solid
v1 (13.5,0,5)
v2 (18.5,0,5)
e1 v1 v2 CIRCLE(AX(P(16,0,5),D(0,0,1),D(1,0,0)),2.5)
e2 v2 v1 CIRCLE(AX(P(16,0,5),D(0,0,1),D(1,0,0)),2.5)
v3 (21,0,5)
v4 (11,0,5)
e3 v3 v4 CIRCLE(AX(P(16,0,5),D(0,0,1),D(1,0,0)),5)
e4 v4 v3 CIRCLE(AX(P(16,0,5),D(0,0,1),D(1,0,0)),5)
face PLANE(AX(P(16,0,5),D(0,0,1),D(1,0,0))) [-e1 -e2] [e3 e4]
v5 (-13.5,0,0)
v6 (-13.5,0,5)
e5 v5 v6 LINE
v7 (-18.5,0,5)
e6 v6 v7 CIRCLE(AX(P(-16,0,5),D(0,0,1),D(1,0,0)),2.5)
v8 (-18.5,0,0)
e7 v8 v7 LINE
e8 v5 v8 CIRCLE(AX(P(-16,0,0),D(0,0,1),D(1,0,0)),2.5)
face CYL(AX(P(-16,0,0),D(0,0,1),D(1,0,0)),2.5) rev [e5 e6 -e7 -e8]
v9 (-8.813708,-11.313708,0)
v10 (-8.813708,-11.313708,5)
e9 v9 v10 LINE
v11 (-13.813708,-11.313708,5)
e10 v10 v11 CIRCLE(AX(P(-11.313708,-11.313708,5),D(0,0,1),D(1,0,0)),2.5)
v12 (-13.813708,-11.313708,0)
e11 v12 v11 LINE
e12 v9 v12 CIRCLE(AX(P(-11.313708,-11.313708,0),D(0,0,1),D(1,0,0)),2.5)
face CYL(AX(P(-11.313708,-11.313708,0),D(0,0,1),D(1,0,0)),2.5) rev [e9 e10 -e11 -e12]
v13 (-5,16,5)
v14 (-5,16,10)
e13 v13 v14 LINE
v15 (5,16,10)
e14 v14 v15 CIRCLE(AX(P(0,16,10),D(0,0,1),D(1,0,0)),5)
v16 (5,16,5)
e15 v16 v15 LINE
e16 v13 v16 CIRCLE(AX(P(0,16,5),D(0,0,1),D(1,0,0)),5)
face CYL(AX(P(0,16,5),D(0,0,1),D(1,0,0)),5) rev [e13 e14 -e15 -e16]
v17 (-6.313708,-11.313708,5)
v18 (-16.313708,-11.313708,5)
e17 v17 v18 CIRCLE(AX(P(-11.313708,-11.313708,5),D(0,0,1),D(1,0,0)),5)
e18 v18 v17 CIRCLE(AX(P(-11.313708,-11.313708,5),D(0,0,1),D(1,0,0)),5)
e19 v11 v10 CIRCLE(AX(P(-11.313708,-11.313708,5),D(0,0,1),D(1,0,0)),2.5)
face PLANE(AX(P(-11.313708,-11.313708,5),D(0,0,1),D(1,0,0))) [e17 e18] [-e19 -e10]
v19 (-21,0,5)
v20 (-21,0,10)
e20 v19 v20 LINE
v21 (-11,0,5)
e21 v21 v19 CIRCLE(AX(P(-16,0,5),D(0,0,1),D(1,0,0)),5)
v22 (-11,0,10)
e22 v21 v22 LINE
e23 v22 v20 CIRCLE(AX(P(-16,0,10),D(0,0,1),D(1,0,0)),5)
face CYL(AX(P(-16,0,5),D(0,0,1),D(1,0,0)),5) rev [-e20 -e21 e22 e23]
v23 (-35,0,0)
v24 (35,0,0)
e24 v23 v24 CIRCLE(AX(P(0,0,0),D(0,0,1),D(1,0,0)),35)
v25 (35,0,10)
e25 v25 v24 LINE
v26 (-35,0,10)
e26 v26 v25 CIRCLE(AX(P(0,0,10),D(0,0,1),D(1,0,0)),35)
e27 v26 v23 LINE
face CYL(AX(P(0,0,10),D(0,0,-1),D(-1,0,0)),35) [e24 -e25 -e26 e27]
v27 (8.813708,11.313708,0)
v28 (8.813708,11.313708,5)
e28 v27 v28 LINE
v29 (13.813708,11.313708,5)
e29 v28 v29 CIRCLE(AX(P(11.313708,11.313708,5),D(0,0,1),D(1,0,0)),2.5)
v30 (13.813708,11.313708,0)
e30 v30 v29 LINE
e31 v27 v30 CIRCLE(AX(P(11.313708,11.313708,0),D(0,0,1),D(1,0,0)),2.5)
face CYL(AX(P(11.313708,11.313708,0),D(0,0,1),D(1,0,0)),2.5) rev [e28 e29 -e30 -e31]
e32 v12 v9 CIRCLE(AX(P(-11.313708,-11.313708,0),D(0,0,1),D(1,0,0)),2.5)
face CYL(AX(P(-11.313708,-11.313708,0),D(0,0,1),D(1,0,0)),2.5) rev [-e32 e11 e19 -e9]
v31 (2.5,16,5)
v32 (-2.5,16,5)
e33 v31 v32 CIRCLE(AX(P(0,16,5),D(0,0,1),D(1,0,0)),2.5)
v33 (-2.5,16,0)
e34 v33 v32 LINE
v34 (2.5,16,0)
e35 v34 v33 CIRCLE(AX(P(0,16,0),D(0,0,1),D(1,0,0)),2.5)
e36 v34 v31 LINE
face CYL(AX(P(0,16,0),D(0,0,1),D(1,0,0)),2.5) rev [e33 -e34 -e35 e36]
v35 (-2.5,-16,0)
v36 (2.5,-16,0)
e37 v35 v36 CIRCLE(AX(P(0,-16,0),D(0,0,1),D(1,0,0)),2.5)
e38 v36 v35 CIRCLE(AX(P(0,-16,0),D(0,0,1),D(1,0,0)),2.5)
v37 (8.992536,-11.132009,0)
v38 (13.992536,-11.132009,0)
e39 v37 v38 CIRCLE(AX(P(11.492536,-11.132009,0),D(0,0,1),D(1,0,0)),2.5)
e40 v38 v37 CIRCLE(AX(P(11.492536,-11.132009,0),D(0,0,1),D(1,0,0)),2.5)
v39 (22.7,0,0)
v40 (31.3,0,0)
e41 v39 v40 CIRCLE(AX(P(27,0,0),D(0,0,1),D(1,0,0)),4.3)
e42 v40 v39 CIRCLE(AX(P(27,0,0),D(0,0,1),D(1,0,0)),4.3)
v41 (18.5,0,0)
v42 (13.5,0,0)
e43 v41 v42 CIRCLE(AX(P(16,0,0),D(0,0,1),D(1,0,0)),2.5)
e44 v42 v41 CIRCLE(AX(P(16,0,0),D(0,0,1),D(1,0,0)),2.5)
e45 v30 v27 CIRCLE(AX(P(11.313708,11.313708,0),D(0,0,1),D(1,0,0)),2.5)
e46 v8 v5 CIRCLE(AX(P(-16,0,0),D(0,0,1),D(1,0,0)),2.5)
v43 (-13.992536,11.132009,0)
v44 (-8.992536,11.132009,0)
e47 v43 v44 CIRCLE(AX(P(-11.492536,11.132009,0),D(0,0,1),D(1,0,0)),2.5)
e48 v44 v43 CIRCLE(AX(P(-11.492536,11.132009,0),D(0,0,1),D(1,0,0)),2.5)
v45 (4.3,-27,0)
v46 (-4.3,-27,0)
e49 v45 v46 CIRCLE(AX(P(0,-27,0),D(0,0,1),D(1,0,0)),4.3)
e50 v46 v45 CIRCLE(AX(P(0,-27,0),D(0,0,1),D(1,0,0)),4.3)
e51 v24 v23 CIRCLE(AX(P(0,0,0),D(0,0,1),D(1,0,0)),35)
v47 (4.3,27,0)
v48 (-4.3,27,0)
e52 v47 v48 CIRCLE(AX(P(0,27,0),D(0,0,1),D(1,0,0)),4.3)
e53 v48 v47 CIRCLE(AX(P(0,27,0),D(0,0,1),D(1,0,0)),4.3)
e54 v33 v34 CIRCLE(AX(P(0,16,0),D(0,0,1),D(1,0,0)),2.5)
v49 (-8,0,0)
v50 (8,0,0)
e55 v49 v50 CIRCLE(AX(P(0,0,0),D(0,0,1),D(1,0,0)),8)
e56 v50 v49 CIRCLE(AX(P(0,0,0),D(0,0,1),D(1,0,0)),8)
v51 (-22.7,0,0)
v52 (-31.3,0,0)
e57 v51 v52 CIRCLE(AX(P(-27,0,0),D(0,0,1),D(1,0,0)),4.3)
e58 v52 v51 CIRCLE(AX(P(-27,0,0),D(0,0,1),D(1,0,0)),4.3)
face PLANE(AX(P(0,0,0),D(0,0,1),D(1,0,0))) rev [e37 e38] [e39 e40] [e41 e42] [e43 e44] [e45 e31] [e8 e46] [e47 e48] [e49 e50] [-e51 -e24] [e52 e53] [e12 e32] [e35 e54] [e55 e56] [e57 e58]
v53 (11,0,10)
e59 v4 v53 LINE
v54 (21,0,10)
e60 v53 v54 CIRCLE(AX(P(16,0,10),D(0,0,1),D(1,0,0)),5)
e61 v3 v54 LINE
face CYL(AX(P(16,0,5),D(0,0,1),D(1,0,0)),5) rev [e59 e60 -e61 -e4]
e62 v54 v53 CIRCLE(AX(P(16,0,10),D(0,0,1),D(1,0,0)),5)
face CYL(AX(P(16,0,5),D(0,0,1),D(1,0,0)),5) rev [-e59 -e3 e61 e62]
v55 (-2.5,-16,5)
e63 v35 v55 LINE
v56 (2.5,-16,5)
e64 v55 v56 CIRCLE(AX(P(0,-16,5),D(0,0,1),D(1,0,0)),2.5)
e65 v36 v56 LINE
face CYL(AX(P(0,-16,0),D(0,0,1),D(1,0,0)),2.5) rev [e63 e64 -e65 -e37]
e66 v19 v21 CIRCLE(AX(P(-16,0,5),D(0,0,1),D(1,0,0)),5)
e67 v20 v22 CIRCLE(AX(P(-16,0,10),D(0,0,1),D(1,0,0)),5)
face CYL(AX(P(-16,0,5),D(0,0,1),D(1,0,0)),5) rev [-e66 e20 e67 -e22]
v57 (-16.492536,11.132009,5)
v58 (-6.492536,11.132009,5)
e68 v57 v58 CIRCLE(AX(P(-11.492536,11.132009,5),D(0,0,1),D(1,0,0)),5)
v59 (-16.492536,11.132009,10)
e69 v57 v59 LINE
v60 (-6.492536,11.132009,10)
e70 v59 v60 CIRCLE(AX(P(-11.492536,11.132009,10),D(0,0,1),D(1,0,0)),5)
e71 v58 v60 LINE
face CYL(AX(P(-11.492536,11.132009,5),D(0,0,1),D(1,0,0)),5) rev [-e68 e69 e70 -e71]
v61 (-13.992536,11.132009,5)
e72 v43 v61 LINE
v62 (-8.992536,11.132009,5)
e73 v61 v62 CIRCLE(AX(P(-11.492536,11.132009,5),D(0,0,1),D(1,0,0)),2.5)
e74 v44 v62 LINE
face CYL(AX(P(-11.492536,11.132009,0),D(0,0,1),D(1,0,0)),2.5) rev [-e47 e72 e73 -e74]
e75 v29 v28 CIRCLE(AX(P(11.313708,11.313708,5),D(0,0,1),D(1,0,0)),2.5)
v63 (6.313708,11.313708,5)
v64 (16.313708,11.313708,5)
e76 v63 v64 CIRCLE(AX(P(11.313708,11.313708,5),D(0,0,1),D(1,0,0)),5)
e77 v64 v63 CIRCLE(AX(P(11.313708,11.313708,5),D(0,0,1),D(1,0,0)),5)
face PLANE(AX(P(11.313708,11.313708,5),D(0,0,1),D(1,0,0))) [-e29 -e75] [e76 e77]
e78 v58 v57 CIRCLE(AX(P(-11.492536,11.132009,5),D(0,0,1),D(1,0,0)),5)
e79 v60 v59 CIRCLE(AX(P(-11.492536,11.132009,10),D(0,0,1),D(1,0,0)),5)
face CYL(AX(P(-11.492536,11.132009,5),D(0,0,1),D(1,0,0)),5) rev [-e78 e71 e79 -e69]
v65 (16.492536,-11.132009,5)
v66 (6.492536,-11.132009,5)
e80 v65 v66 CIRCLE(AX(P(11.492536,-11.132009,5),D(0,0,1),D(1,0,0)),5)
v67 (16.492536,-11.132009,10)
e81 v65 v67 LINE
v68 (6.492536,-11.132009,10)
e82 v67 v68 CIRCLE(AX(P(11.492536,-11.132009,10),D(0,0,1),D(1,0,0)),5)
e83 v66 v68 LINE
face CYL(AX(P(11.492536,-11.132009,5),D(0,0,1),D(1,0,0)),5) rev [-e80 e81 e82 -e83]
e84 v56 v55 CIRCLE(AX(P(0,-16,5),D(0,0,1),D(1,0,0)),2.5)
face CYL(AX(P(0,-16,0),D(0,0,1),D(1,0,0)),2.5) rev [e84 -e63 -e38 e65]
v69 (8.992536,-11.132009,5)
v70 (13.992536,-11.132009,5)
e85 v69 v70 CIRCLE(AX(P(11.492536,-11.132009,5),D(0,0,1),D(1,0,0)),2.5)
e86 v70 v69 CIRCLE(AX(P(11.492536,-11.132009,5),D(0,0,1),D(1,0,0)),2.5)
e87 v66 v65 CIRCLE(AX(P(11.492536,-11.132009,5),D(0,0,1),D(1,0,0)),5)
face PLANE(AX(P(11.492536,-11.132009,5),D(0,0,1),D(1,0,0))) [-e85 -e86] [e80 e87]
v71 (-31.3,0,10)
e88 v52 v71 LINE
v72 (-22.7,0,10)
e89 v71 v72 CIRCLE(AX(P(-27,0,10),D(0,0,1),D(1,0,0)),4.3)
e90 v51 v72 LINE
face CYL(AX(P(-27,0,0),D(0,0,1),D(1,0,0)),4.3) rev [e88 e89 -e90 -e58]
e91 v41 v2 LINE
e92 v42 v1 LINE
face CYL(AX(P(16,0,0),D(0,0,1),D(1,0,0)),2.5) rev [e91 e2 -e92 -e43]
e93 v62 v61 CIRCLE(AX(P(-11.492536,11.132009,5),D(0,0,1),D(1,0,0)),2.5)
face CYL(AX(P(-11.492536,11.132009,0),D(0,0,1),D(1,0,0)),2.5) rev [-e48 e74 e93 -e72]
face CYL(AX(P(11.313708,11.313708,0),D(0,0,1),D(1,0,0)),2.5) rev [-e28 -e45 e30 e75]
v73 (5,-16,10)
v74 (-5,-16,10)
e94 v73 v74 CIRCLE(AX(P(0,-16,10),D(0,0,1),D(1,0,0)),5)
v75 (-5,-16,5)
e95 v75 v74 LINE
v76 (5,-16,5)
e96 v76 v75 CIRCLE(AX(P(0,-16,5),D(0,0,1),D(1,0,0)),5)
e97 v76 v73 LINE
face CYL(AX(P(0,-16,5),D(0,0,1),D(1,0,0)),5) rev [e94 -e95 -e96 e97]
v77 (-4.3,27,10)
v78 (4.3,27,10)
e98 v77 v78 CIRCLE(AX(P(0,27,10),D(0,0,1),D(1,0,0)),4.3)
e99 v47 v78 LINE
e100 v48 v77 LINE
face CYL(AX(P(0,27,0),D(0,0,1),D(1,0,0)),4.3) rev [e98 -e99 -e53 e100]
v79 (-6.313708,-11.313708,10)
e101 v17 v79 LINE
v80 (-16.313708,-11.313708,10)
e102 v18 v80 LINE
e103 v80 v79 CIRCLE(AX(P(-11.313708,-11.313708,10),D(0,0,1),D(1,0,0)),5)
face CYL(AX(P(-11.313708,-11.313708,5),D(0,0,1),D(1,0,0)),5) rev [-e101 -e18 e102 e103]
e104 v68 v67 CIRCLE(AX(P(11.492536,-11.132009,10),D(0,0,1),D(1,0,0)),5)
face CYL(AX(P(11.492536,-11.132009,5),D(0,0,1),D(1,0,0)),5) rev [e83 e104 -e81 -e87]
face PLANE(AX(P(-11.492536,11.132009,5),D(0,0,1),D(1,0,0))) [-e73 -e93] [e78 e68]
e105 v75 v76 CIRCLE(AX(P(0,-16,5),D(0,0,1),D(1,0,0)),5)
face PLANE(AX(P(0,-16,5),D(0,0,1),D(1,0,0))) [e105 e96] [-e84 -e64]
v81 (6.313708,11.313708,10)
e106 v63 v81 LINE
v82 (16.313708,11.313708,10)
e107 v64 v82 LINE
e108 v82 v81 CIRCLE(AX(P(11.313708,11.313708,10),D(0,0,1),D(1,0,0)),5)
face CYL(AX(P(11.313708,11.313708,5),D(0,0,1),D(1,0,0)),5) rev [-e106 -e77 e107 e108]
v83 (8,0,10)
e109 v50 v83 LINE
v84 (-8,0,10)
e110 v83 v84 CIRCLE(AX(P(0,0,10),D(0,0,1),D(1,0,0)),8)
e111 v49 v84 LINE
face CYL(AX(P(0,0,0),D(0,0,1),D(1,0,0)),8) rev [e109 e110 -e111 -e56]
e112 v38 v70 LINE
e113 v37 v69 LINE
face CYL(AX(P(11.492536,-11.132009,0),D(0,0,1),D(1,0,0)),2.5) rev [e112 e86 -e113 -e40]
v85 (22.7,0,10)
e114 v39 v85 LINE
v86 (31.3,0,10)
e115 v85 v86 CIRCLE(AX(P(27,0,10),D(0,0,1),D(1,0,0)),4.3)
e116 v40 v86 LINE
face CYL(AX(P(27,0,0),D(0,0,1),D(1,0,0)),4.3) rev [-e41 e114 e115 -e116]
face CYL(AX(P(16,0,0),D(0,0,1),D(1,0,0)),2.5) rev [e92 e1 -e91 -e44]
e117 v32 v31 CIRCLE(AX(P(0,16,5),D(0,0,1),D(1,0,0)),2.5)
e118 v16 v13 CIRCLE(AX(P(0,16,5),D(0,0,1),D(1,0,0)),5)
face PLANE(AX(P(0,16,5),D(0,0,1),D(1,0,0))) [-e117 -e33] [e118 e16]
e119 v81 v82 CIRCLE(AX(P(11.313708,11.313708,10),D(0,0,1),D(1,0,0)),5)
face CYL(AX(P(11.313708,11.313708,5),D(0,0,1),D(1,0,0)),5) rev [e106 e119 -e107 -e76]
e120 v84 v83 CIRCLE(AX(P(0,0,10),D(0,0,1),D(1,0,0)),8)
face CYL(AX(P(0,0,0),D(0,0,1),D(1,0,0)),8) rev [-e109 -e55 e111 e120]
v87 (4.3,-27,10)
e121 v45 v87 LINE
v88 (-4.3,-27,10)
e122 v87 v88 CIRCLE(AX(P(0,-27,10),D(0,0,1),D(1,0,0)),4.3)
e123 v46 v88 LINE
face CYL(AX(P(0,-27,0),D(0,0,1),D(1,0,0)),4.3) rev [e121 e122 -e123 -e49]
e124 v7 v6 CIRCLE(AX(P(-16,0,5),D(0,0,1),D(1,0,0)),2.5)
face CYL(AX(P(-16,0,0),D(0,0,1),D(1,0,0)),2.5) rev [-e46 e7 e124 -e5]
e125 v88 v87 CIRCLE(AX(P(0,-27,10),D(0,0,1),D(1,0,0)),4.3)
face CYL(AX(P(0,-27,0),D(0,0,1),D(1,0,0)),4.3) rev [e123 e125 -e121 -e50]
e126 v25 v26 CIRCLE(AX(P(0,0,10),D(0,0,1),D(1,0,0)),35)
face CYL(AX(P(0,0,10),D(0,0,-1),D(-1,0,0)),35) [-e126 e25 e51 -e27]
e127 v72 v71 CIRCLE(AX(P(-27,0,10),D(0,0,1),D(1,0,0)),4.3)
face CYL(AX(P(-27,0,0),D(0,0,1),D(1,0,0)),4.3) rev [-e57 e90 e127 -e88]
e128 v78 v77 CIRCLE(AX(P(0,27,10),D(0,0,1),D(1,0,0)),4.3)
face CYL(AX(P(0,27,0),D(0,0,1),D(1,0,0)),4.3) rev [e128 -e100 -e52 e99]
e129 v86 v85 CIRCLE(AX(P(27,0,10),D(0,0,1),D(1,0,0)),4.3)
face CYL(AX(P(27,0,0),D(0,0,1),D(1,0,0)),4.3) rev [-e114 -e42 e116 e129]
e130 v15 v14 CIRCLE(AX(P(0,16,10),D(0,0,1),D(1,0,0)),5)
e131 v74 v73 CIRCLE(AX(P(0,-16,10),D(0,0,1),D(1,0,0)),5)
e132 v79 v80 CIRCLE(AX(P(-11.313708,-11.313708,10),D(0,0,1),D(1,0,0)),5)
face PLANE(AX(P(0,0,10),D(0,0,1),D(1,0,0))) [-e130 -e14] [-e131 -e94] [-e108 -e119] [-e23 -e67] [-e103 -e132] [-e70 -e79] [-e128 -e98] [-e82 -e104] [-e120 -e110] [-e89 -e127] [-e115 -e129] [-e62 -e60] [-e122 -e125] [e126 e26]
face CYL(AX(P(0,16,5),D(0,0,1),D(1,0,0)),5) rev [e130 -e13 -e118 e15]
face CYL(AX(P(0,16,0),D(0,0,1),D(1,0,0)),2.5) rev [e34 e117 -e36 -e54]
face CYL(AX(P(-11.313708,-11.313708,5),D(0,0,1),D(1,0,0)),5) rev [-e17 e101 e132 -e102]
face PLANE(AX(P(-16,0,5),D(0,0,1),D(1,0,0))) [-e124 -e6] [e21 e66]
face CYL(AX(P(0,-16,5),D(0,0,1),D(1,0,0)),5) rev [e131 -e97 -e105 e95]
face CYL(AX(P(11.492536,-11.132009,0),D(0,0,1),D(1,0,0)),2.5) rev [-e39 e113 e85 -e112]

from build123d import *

# Parameters (mm, degrees)
DISC_PROFILE_70_R                  = 35
DISC_70_X_10_DEPTH                 = 10
CENTRE_BORE_PROFILE_16_R           = 8
CENTRE_BORE_16_DEPTH               = 10
OUTER_HOLES_PROFILE_4X_8_6_R       = 4.3
OUTER_HOLES_4X_8_6_DEPTH           = 10
COUNTERBORE_PROFILE_R              = 5
COUNTERBORES_DEPTH_5_DEPTH         = 5
COUNTERBORE_THROUGH_HOLE_PROFILE_R = 2.5
COUNTERBORE_THROUGH_HOLES_DEPTH    = 5


with BuildPart() as part:
    # Disc Profile Ø70 → Disc Ø70 x 10 (new body)
    with BuildSketch(Plane.XY):
        Circle(DISC_PROFILE_70_R)
    extrude(amount=DISC_70_X_10_DEPTH)

    # Centre Bore Profile Ø16 → Centre Bore Ø16 (cut)
    with BuildSketch(Plane.XY.offset(10)):
        Circle(CENTRE_BORE_PROFILE_16_R)
    extrude(amount=-CENTRE_BORE_16_DEPTH, mode=Mode.SUBTRACT)

    # Outer Holes Profile 4xØ8.6 → Outer Holes 4xØ8.6 (cut)
    with BuildSketch(Plane.XY.offset(10)):
        with Locations((0, 27)):
            Circle(OUTER_HOLES_PROFILE_4X_8_6_R)
        with Locations((27, 0)):
            Circle(OUTER_HOLES_PROFILE_4X_8_6_R)
        with Locations((0, -27)):
            Circle(OUTER_HOLES_PROFILE_4X_8_6_R)
        with Locations((-27, 0)):
            Circle(OUTER_HOLES_PROFILE_4X_8_6_R)
    extrude(amount=-OUTER_HOLES_4X_8_6_DEPTH, mode=Mode.SUBTRACT)

    # Counterbore Profile → Counterbores Depth 5 (cut)
    with BuildSketch(Plane.XY.offset(10)):
        with Locations((0, 16)):
            Circle(COUNTERBORE_PROFILE_R)
        with Locations((16, 0)):
            Circle(COUNTERBORE_PROFILE_R)
        with Locations((0, -16)):
            Circle(COUNTERBORE_PROFILE_R)
        with Locations((-16, 0)):
            Circle(COUNTERBORE_PROFILE_R)
        with Locations((11.492535714, -11.132008932)):
            Circle(COUNTERBORE_PROFILE_R)
        with Locations((11.313708499, 11.313708499)):
            Circle(COUNTERBORE_PROFILE_R)
        with Locations((-11.492535714, 11.132008932)):
            Circle(COUNTERBORE_PROFILE_R)
        with Locations((-11.313708499, -11.313708499)):
            Circle(COUNTERBORE_PROFILE_R)
    extrude(amount=-COUNTERBORES_DEPTH_5_DEPTH, mode=Mode.SUBTRACT)

    # Counterbore Through Hole Profile → Counterbore Through Holes (cut)
    with BuildSketch(Plane.XY.offset(5)):
        with Locations((0, 16)):
            Circle(COUNTERBORE_THROUGH_HOLE_PROFILE_R)
        with Locations((11.313708499, 11.313708499)):
            Circle(COUNTERBORE_THROUGH_HOLE_PROFILE_R)
        with Locations((16, 0)):
            Circle(COUNTERBORE_THROUGH_HOLE_PROFILE_R)
        with Locations((11.492535714, -11.132008932)):
            Circle(COUNTERBORE_THROUGH_HOLE_PROFILE_R)
        with Locations((0, -16)):
            Circle(COUNTERBORE_THROUGH_HOLE_PROFILE_R)
        with Locations((-11.313708499, -11.313708499)):
            Circle(COUNTERBORE_THROUGH_HOLE_PROFILE_R)
        with Locations((-16, 0)):
            Circle(COUNTERBORE_THROUGH_HOLE_PROFILE_R)
        with Locations((-11.492535714, 11.132008932)):
            Circle(COUNTERBORE_THROUGH_HOLE_PROFILE_R)
    extrude(amount=-COUNTERBORE_THROUGH_HOLES_DEPTH, mode=Mode.SUBTRACT)


solid = part.part
